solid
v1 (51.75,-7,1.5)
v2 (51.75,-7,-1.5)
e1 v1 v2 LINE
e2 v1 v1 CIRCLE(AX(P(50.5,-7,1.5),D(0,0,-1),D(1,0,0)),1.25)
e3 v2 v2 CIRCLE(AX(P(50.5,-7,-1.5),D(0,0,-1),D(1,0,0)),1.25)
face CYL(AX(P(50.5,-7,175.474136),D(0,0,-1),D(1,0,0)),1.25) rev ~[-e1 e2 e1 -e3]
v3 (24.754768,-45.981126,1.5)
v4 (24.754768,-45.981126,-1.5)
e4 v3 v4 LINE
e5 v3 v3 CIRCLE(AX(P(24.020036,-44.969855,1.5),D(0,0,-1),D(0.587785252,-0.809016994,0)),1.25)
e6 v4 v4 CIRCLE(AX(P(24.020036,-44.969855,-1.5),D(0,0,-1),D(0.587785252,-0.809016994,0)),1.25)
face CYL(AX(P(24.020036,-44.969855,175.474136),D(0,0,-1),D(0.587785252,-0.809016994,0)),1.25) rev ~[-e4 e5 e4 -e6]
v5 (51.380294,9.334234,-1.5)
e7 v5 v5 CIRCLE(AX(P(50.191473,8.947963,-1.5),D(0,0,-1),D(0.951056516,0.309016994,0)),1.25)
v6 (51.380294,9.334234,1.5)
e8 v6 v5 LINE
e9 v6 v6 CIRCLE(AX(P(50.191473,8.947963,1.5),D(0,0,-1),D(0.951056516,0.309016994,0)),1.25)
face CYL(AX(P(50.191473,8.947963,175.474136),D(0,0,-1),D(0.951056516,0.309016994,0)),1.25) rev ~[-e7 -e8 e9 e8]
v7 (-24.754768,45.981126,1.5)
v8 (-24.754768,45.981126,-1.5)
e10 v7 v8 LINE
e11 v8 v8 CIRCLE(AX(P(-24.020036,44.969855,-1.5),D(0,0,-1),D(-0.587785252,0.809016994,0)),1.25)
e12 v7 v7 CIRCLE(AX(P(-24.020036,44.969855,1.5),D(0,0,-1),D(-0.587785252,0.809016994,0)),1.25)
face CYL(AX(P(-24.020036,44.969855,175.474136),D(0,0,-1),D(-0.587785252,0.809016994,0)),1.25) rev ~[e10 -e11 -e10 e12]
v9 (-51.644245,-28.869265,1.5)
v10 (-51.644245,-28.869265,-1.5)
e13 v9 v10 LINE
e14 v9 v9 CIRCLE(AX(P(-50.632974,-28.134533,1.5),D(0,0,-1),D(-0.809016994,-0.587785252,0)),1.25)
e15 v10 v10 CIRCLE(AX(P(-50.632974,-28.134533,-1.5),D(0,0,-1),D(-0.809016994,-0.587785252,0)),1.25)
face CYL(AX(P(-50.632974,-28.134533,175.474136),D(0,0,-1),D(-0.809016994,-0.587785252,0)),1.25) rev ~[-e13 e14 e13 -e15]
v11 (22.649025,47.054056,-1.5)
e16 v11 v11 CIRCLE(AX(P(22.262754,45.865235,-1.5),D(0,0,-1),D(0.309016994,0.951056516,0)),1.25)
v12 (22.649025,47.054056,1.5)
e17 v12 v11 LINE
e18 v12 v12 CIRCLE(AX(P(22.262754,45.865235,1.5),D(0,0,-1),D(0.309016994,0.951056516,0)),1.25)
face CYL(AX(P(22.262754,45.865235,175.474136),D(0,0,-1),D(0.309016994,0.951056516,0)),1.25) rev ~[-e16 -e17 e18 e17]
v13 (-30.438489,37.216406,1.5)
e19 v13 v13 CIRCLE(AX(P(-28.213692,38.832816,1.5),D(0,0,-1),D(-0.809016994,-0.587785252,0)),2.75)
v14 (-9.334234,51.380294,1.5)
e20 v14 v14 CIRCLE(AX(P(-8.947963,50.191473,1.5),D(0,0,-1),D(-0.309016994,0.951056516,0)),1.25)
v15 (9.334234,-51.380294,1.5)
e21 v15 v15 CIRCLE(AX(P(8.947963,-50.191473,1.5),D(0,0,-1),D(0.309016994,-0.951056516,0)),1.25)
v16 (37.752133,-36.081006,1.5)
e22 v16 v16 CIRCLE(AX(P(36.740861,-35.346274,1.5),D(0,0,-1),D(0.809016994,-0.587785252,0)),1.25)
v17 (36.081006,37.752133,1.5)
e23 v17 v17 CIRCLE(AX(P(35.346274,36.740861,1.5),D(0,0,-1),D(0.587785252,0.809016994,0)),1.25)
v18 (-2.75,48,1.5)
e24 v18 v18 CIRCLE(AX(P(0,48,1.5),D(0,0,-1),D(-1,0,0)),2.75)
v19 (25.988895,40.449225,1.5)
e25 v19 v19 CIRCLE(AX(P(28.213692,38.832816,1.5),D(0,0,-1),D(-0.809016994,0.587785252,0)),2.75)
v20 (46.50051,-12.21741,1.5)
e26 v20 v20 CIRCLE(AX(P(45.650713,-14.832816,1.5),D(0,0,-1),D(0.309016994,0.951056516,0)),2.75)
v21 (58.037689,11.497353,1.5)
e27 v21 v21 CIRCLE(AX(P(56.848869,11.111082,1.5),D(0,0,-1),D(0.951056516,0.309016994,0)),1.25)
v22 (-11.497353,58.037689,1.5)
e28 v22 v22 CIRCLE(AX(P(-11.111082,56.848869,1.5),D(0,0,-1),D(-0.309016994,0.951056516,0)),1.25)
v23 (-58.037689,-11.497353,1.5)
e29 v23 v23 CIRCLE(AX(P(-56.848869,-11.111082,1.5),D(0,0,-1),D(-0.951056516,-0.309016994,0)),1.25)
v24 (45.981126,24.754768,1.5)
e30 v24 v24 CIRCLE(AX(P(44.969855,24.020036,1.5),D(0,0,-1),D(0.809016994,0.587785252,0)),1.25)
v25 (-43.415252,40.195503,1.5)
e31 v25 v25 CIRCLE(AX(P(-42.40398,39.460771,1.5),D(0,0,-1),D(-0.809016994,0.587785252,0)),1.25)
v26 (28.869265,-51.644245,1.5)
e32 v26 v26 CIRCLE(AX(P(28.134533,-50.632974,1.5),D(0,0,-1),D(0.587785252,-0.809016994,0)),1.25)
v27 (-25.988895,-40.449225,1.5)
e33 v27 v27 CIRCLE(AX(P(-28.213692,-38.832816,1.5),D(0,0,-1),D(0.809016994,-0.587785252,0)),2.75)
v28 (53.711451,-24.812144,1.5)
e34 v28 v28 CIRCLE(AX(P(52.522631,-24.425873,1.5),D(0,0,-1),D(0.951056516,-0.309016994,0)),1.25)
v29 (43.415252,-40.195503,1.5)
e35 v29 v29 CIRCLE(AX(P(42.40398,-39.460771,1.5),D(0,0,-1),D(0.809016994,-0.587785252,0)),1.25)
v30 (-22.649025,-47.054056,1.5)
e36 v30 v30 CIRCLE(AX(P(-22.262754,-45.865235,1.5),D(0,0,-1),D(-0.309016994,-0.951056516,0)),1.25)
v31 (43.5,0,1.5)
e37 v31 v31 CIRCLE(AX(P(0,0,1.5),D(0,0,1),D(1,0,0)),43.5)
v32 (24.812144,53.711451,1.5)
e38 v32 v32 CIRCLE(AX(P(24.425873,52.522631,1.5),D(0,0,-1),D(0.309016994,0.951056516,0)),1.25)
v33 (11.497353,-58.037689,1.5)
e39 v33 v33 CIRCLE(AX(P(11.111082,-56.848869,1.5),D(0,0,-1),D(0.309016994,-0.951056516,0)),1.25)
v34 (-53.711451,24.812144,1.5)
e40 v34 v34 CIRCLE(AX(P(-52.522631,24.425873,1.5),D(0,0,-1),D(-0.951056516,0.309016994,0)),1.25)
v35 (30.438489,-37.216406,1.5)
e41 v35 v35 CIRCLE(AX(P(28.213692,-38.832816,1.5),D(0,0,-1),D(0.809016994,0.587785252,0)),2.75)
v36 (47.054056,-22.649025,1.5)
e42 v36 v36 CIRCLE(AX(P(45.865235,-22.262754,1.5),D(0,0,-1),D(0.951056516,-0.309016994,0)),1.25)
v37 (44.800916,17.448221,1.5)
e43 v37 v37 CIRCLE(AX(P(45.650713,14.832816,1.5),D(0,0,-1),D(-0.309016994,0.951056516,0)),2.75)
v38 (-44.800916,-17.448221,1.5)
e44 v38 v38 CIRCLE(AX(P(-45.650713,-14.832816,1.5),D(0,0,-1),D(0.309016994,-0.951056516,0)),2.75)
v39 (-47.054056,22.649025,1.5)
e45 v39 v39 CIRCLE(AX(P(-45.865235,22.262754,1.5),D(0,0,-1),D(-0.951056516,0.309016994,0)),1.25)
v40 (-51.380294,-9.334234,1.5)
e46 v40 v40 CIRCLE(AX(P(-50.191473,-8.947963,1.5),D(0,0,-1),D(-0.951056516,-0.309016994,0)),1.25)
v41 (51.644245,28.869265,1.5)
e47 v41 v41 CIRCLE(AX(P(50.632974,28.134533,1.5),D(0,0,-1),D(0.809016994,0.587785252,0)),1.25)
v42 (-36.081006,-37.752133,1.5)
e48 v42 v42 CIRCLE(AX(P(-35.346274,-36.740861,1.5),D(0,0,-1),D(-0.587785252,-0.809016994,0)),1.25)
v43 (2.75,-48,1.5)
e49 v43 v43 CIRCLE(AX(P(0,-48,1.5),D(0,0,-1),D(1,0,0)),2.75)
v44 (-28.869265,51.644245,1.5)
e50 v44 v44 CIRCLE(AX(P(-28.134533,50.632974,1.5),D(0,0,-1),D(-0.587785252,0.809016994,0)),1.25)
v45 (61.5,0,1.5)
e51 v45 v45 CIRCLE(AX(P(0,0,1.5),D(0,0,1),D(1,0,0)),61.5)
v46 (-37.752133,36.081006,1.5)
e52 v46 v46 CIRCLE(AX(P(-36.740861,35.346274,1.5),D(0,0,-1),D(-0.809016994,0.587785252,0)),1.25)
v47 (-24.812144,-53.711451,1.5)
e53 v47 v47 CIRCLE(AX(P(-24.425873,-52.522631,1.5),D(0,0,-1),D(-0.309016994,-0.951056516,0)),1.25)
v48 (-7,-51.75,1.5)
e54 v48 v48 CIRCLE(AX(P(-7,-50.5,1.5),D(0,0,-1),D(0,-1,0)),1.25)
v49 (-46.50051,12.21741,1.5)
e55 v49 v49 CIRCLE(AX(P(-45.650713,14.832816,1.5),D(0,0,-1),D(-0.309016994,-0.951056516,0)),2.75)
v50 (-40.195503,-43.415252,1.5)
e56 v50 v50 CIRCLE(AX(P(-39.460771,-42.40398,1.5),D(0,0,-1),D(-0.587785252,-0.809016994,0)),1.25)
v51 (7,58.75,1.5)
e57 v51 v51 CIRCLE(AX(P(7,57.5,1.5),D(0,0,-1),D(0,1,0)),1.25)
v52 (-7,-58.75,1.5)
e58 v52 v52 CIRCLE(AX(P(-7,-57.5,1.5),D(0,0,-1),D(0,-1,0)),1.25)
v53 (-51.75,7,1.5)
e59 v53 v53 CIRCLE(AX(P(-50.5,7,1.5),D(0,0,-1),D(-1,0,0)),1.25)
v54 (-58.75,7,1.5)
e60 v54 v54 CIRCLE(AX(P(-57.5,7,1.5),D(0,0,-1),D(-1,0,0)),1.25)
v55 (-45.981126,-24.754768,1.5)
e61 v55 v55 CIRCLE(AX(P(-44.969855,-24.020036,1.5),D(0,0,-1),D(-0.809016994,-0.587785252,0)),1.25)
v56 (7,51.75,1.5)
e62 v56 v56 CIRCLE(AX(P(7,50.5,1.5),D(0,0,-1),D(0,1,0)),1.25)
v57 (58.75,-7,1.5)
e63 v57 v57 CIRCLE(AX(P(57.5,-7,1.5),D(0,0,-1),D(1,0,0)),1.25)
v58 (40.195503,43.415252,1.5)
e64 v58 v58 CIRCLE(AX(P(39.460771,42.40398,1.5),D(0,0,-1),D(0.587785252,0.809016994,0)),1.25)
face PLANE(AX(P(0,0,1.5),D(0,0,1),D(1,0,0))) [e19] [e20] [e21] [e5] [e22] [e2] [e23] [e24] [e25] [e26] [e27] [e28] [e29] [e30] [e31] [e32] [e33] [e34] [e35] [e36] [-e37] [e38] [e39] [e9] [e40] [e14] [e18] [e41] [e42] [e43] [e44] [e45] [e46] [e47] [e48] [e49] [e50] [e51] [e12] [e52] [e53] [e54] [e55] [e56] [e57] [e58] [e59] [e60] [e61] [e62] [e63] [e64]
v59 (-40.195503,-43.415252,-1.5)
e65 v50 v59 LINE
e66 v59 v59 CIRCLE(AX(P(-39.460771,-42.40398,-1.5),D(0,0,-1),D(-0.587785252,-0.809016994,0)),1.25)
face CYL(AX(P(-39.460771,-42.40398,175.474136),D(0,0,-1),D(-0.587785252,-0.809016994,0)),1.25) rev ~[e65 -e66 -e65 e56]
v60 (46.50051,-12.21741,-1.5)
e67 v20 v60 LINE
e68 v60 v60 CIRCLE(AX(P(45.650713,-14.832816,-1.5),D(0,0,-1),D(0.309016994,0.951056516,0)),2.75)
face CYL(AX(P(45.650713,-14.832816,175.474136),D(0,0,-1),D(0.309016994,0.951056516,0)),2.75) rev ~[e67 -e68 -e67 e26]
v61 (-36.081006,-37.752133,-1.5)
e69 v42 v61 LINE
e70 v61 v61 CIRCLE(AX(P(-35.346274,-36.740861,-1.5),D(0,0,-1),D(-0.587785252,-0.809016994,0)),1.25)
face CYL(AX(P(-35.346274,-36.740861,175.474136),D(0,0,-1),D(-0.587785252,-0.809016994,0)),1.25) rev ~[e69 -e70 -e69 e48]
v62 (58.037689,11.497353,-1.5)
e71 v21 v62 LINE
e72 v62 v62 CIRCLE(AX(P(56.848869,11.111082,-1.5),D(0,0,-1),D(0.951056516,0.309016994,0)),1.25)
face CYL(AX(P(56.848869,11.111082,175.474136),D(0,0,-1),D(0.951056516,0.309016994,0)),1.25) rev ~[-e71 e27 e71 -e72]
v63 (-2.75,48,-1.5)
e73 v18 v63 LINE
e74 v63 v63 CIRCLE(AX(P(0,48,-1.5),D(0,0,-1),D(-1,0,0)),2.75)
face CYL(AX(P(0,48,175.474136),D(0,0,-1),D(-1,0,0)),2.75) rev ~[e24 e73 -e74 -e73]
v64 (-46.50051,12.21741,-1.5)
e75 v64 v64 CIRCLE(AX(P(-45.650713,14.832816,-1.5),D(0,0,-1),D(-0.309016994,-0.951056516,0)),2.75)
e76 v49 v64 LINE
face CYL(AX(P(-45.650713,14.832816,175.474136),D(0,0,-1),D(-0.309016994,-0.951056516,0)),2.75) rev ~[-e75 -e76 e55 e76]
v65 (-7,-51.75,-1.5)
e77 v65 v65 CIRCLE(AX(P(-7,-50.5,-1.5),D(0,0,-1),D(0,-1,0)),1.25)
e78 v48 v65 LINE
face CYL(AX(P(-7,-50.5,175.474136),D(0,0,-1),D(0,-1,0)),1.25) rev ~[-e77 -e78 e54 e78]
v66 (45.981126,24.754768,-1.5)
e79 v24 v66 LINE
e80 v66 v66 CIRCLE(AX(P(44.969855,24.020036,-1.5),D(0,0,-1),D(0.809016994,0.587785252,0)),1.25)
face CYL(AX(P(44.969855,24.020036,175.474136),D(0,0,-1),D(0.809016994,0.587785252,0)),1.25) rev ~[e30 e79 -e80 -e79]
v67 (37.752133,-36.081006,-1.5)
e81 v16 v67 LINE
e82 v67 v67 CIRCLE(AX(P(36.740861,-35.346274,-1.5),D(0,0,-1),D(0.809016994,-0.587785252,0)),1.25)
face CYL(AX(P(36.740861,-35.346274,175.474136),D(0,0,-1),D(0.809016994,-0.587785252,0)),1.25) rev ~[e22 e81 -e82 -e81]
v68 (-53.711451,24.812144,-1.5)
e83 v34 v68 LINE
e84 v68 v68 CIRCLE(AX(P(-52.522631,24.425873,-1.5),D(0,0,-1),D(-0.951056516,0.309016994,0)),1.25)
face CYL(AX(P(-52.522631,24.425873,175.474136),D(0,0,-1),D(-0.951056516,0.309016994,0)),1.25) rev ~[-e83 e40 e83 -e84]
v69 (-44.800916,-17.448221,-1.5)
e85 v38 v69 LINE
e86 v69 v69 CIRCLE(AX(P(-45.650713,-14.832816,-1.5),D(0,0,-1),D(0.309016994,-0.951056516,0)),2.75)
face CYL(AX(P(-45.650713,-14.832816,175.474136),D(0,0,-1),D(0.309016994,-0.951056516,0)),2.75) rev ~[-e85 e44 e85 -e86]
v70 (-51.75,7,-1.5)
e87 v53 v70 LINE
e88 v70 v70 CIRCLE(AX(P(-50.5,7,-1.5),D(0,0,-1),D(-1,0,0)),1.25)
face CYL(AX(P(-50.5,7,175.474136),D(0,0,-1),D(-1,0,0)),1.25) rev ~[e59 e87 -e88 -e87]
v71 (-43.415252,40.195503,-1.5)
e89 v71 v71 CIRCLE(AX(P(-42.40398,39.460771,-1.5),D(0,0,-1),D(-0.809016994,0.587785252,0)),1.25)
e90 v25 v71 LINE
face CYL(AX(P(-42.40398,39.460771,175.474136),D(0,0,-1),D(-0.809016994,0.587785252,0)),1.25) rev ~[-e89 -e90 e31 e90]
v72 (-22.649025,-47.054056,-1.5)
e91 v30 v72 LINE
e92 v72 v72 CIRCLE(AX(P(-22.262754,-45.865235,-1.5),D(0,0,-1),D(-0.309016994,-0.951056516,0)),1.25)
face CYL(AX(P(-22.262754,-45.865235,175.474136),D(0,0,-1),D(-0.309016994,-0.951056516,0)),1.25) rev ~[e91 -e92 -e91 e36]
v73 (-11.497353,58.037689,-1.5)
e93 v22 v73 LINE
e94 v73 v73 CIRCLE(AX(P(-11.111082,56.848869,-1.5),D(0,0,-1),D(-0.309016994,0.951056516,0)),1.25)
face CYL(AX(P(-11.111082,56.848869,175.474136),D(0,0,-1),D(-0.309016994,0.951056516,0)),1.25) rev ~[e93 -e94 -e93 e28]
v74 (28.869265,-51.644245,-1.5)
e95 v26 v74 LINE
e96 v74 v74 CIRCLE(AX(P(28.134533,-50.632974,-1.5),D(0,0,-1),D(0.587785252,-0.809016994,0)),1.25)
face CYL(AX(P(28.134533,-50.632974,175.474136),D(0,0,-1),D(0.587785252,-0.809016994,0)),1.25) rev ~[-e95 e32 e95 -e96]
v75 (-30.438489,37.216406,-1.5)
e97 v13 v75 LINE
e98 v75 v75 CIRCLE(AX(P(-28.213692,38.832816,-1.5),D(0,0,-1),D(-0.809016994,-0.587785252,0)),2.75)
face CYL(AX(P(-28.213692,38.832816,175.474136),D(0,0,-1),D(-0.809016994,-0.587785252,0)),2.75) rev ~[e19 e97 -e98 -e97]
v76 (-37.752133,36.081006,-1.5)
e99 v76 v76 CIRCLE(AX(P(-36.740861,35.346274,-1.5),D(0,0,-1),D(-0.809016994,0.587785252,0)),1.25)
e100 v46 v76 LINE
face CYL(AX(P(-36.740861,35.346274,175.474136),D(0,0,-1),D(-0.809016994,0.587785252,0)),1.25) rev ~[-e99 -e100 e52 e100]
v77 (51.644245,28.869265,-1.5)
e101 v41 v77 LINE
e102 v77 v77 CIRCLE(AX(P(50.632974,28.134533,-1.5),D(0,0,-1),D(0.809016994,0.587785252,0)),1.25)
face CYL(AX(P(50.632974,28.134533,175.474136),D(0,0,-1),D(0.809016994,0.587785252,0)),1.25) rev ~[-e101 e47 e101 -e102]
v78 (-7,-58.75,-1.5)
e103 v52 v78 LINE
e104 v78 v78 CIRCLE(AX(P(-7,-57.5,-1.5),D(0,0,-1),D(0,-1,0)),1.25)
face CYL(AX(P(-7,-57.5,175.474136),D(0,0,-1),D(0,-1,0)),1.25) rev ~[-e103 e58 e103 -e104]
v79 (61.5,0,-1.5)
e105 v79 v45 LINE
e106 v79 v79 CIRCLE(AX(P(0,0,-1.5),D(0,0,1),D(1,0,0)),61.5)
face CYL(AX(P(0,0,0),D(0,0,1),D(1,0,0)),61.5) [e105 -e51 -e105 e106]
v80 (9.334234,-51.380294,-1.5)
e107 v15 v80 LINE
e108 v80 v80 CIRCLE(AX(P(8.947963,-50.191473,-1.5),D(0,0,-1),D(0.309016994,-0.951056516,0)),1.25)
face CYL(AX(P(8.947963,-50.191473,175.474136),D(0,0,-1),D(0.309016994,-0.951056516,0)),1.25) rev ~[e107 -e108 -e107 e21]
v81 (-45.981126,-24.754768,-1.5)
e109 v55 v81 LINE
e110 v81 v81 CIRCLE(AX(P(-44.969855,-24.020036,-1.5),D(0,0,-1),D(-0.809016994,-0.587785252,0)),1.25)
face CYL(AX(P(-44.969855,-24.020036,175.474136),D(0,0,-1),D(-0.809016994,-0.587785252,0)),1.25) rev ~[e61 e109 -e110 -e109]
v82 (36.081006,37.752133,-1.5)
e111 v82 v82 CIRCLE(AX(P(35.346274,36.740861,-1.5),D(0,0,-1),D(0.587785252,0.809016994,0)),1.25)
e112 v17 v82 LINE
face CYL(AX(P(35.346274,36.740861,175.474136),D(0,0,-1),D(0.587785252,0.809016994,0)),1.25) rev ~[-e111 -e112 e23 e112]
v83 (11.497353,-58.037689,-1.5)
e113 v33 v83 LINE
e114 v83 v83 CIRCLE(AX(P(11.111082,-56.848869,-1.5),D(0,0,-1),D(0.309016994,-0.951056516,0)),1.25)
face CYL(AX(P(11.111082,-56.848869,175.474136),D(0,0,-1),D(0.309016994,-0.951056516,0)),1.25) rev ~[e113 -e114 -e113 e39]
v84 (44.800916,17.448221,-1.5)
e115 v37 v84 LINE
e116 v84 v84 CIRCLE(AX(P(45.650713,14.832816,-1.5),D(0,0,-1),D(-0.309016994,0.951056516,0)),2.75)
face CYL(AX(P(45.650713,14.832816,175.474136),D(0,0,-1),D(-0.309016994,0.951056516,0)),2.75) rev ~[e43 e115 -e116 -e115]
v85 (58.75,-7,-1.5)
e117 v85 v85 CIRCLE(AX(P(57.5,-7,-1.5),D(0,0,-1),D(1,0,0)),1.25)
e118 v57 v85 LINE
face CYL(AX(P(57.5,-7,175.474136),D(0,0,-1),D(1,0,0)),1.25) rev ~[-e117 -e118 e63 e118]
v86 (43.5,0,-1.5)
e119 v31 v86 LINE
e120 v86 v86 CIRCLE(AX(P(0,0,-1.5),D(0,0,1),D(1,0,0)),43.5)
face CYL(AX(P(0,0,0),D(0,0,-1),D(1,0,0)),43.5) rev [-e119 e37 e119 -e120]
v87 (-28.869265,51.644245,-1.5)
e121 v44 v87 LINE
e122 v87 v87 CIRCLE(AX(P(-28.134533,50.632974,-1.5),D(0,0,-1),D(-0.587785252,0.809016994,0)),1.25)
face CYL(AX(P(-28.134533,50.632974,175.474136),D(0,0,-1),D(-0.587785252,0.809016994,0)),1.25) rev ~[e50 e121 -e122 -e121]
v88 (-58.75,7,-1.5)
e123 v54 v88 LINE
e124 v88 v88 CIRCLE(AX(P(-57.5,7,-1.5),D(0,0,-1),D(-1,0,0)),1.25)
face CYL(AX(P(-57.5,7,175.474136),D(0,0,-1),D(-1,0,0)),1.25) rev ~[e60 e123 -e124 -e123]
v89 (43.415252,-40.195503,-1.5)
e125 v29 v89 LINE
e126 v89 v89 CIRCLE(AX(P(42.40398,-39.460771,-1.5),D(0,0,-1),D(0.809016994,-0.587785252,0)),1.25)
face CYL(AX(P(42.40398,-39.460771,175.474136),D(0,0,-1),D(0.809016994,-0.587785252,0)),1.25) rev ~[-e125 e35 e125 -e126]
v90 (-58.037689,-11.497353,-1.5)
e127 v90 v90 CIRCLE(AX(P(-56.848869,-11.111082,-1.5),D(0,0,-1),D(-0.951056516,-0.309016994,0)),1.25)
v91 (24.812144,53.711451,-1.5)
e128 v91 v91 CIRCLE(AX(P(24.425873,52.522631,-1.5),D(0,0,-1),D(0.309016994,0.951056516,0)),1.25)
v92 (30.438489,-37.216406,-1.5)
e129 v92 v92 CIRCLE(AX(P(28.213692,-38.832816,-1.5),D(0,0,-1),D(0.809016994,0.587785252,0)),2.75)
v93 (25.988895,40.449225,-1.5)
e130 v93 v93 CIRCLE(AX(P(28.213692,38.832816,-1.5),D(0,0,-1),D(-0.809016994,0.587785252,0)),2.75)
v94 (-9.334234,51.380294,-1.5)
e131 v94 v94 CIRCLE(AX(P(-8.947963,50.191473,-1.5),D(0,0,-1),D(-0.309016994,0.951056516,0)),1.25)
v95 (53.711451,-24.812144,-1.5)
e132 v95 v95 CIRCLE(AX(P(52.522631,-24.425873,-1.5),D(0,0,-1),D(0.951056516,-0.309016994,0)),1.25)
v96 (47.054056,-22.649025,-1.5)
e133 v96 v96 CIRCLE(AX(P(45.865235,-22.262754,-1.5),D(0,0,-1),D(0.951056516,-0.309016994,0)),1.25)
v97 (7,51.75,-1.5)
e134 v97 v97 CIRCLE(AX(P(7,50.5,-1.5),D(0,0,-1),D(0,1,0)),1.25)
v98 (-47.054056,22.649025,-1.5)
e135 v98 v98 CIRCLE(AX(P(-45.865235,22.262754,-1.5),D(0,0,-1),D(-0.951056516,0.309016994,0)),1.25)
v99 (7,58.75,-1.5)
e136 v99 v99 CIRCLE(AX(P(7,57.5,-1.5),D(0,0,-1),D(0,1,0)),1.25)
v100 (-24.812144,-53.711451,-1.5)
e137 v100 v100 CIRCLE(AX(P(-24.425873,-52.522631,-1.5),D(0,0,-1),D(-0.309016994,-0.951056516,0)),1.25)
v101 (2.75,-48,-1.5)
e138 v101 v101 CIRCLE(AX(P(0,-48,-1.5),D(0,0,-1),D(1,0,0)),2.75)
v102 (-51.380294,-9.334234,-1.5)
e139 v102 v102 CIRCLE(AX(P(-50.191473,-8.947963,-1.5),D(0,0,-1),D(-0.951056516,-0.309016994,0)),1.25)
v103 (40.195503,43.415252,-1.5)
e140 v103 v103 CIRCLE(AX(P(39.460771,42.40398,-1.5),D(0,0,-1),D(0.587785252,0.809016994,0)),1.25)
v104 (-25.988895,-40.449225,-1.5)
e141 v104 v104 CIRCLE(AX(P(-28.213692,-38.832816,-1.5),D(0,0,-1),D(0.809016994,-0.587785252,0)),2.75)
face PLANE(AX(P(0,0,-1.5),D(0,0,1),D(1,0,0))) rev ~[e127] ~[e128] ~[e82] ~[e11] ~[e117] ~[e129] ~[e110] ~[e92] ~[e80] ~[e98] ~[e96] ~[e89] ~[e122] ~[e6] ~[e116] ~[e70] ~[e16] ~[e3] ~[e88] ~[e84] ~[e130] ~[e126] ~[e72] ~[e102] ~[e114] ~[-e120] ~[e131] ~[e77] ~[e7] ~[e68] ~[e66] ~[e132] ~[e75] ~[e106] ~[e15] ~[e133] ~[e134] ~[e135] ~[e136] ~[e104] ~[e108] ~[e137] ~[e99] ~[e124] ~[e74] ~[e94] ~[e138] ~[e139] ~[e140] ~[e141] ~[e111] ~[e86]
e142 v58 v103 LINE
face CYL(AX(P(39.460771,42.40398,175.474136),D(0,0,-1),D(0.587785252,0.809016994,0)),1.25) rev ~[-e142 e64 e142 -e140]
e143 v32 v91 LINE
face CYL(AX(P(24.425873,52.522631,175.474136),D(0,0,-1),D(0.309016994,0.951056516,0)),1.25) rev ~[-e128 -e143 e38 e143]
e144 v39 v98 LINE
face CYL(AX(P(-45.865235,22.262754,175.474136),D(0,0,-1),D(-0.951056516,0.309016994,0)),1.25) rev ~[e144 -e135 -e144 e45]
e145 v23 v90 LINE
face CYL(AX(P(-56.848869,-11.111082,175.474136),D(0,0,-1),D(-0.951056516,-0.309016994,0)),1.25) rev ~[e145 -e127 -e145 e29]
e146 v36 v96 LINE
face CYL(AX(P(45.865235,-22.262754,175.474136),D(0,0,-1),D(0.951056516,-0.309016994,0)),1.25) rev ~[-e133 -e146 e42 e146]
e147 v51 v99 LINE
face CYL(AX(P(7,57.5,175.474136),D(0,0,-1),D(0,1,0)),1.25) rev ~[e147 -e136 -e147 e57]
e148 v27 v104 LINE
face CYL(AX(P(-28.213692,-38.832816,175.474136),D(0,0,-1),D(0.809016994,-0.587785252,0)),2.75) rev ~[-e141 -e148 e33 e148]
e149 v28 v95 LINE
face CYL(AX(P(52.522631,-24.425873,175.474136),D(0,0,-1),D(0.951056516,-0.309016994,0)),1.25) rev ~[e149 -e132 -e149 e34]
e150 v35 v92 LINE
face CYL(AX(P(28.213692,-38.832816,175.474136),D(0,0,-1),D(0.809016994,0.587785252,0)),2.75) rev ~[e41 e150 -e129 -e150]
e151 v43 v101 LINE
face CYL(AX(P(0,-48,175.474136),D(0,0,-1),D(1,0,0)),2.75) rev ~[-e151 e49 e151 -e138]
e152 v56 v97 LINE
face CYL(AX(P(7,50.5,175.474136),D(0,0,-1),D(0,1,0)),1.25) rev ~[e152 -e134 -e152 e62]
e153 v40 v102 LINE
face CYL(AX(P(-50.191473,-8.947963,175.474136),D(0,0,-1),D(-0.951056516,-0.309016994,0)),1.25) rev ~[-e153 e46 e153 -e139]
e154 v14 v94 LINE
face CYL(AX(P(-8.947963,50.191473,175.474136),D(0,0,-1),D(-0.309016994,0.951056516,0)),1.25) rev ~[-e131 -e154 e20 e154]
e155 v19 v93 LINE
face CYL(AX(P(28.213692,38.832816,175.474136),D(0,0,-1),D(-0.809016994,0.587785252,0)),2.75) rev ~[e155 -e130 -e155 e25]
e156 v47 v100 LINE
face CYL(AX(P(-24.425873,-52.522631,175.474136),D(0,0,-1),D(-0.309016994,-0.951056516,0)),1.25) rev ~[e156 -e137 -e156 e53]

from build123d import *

# Parameters (mm, degrees)
SKETCH_1_R               = 61.5
SKETCH_1_R_2             = 43.5
EXTRUDE_1_DEPTH          = 1.5
HOLE_WIZARD_5_5_5_5_2_D  = 5.5
HOLE_WIZARD_M3_1_D       = 2.5
PATTERN_CIRCULAR_1_COUNT = 10
PATTERN_CIRCULAR_2_COUNT = 20


with BuildPart() as part:
    # 草图1 → 凸台-拉伸1 (new, symmetric)
    with BuildSketch(Plane.XY):
        Circle(SKETCH_1_R)
        Circle(SKETCH_1_R_2, mode=Mode.SUBTRACT)
    extrude(amount=EXTRUDE_1_DEPTH, both=True)

    # Ø5.5 (5.5) 直径孔2 (through all)
    with Locations(Plane.XY.offset(1.5)):
        with Locations((0, 48)):
            hole_wizard_5_5_5_5_2 = Hole(HOLE_WIZARD_5_5_5_5_2_D / 2)

    # M3 螺纹孔1 (through all)
    with Locations(Plane.XY.offset(1.5)):
        with Locations((-57.5, 7), (-50.5, 7)):
            hole_wizard_m3_1 = Hole(HOLE_WIZARD_M3_1_D / 2)

    # 阵列(圆周)1: Ø5.5 (5.5) 直径孔2 ×10 about axis
    pattern_circular_1_axis = Axis((0, 0, 0), (0, 0, 1))
    for i in range(1, PATTERN_CIRCULAR_1_COUNT):
        add(hole_wizard_5_5_5_5_2.rotate(pattern_circular_1_axis, i * 360 / PATTERN_CIRCULAR_1_COUNT), mode=Mode.SUBTRACT)

    # 阵列(圆周)2: M3 螺纹孔1 ×20 about axis
    pattern_circular_2_axis = Axis((0, 0, 0), (0, 0, 1))
    for i in range(1, PATTERN_CIRCULAR_2_COUNT):
        add(hole_wizard_m3_1.rotate(pattern_circular_2_axis, i * 360 / PATTERN_CIRCULAR_2_COUNT), mode=Mode.SUBTRACT)


solid = part.part
